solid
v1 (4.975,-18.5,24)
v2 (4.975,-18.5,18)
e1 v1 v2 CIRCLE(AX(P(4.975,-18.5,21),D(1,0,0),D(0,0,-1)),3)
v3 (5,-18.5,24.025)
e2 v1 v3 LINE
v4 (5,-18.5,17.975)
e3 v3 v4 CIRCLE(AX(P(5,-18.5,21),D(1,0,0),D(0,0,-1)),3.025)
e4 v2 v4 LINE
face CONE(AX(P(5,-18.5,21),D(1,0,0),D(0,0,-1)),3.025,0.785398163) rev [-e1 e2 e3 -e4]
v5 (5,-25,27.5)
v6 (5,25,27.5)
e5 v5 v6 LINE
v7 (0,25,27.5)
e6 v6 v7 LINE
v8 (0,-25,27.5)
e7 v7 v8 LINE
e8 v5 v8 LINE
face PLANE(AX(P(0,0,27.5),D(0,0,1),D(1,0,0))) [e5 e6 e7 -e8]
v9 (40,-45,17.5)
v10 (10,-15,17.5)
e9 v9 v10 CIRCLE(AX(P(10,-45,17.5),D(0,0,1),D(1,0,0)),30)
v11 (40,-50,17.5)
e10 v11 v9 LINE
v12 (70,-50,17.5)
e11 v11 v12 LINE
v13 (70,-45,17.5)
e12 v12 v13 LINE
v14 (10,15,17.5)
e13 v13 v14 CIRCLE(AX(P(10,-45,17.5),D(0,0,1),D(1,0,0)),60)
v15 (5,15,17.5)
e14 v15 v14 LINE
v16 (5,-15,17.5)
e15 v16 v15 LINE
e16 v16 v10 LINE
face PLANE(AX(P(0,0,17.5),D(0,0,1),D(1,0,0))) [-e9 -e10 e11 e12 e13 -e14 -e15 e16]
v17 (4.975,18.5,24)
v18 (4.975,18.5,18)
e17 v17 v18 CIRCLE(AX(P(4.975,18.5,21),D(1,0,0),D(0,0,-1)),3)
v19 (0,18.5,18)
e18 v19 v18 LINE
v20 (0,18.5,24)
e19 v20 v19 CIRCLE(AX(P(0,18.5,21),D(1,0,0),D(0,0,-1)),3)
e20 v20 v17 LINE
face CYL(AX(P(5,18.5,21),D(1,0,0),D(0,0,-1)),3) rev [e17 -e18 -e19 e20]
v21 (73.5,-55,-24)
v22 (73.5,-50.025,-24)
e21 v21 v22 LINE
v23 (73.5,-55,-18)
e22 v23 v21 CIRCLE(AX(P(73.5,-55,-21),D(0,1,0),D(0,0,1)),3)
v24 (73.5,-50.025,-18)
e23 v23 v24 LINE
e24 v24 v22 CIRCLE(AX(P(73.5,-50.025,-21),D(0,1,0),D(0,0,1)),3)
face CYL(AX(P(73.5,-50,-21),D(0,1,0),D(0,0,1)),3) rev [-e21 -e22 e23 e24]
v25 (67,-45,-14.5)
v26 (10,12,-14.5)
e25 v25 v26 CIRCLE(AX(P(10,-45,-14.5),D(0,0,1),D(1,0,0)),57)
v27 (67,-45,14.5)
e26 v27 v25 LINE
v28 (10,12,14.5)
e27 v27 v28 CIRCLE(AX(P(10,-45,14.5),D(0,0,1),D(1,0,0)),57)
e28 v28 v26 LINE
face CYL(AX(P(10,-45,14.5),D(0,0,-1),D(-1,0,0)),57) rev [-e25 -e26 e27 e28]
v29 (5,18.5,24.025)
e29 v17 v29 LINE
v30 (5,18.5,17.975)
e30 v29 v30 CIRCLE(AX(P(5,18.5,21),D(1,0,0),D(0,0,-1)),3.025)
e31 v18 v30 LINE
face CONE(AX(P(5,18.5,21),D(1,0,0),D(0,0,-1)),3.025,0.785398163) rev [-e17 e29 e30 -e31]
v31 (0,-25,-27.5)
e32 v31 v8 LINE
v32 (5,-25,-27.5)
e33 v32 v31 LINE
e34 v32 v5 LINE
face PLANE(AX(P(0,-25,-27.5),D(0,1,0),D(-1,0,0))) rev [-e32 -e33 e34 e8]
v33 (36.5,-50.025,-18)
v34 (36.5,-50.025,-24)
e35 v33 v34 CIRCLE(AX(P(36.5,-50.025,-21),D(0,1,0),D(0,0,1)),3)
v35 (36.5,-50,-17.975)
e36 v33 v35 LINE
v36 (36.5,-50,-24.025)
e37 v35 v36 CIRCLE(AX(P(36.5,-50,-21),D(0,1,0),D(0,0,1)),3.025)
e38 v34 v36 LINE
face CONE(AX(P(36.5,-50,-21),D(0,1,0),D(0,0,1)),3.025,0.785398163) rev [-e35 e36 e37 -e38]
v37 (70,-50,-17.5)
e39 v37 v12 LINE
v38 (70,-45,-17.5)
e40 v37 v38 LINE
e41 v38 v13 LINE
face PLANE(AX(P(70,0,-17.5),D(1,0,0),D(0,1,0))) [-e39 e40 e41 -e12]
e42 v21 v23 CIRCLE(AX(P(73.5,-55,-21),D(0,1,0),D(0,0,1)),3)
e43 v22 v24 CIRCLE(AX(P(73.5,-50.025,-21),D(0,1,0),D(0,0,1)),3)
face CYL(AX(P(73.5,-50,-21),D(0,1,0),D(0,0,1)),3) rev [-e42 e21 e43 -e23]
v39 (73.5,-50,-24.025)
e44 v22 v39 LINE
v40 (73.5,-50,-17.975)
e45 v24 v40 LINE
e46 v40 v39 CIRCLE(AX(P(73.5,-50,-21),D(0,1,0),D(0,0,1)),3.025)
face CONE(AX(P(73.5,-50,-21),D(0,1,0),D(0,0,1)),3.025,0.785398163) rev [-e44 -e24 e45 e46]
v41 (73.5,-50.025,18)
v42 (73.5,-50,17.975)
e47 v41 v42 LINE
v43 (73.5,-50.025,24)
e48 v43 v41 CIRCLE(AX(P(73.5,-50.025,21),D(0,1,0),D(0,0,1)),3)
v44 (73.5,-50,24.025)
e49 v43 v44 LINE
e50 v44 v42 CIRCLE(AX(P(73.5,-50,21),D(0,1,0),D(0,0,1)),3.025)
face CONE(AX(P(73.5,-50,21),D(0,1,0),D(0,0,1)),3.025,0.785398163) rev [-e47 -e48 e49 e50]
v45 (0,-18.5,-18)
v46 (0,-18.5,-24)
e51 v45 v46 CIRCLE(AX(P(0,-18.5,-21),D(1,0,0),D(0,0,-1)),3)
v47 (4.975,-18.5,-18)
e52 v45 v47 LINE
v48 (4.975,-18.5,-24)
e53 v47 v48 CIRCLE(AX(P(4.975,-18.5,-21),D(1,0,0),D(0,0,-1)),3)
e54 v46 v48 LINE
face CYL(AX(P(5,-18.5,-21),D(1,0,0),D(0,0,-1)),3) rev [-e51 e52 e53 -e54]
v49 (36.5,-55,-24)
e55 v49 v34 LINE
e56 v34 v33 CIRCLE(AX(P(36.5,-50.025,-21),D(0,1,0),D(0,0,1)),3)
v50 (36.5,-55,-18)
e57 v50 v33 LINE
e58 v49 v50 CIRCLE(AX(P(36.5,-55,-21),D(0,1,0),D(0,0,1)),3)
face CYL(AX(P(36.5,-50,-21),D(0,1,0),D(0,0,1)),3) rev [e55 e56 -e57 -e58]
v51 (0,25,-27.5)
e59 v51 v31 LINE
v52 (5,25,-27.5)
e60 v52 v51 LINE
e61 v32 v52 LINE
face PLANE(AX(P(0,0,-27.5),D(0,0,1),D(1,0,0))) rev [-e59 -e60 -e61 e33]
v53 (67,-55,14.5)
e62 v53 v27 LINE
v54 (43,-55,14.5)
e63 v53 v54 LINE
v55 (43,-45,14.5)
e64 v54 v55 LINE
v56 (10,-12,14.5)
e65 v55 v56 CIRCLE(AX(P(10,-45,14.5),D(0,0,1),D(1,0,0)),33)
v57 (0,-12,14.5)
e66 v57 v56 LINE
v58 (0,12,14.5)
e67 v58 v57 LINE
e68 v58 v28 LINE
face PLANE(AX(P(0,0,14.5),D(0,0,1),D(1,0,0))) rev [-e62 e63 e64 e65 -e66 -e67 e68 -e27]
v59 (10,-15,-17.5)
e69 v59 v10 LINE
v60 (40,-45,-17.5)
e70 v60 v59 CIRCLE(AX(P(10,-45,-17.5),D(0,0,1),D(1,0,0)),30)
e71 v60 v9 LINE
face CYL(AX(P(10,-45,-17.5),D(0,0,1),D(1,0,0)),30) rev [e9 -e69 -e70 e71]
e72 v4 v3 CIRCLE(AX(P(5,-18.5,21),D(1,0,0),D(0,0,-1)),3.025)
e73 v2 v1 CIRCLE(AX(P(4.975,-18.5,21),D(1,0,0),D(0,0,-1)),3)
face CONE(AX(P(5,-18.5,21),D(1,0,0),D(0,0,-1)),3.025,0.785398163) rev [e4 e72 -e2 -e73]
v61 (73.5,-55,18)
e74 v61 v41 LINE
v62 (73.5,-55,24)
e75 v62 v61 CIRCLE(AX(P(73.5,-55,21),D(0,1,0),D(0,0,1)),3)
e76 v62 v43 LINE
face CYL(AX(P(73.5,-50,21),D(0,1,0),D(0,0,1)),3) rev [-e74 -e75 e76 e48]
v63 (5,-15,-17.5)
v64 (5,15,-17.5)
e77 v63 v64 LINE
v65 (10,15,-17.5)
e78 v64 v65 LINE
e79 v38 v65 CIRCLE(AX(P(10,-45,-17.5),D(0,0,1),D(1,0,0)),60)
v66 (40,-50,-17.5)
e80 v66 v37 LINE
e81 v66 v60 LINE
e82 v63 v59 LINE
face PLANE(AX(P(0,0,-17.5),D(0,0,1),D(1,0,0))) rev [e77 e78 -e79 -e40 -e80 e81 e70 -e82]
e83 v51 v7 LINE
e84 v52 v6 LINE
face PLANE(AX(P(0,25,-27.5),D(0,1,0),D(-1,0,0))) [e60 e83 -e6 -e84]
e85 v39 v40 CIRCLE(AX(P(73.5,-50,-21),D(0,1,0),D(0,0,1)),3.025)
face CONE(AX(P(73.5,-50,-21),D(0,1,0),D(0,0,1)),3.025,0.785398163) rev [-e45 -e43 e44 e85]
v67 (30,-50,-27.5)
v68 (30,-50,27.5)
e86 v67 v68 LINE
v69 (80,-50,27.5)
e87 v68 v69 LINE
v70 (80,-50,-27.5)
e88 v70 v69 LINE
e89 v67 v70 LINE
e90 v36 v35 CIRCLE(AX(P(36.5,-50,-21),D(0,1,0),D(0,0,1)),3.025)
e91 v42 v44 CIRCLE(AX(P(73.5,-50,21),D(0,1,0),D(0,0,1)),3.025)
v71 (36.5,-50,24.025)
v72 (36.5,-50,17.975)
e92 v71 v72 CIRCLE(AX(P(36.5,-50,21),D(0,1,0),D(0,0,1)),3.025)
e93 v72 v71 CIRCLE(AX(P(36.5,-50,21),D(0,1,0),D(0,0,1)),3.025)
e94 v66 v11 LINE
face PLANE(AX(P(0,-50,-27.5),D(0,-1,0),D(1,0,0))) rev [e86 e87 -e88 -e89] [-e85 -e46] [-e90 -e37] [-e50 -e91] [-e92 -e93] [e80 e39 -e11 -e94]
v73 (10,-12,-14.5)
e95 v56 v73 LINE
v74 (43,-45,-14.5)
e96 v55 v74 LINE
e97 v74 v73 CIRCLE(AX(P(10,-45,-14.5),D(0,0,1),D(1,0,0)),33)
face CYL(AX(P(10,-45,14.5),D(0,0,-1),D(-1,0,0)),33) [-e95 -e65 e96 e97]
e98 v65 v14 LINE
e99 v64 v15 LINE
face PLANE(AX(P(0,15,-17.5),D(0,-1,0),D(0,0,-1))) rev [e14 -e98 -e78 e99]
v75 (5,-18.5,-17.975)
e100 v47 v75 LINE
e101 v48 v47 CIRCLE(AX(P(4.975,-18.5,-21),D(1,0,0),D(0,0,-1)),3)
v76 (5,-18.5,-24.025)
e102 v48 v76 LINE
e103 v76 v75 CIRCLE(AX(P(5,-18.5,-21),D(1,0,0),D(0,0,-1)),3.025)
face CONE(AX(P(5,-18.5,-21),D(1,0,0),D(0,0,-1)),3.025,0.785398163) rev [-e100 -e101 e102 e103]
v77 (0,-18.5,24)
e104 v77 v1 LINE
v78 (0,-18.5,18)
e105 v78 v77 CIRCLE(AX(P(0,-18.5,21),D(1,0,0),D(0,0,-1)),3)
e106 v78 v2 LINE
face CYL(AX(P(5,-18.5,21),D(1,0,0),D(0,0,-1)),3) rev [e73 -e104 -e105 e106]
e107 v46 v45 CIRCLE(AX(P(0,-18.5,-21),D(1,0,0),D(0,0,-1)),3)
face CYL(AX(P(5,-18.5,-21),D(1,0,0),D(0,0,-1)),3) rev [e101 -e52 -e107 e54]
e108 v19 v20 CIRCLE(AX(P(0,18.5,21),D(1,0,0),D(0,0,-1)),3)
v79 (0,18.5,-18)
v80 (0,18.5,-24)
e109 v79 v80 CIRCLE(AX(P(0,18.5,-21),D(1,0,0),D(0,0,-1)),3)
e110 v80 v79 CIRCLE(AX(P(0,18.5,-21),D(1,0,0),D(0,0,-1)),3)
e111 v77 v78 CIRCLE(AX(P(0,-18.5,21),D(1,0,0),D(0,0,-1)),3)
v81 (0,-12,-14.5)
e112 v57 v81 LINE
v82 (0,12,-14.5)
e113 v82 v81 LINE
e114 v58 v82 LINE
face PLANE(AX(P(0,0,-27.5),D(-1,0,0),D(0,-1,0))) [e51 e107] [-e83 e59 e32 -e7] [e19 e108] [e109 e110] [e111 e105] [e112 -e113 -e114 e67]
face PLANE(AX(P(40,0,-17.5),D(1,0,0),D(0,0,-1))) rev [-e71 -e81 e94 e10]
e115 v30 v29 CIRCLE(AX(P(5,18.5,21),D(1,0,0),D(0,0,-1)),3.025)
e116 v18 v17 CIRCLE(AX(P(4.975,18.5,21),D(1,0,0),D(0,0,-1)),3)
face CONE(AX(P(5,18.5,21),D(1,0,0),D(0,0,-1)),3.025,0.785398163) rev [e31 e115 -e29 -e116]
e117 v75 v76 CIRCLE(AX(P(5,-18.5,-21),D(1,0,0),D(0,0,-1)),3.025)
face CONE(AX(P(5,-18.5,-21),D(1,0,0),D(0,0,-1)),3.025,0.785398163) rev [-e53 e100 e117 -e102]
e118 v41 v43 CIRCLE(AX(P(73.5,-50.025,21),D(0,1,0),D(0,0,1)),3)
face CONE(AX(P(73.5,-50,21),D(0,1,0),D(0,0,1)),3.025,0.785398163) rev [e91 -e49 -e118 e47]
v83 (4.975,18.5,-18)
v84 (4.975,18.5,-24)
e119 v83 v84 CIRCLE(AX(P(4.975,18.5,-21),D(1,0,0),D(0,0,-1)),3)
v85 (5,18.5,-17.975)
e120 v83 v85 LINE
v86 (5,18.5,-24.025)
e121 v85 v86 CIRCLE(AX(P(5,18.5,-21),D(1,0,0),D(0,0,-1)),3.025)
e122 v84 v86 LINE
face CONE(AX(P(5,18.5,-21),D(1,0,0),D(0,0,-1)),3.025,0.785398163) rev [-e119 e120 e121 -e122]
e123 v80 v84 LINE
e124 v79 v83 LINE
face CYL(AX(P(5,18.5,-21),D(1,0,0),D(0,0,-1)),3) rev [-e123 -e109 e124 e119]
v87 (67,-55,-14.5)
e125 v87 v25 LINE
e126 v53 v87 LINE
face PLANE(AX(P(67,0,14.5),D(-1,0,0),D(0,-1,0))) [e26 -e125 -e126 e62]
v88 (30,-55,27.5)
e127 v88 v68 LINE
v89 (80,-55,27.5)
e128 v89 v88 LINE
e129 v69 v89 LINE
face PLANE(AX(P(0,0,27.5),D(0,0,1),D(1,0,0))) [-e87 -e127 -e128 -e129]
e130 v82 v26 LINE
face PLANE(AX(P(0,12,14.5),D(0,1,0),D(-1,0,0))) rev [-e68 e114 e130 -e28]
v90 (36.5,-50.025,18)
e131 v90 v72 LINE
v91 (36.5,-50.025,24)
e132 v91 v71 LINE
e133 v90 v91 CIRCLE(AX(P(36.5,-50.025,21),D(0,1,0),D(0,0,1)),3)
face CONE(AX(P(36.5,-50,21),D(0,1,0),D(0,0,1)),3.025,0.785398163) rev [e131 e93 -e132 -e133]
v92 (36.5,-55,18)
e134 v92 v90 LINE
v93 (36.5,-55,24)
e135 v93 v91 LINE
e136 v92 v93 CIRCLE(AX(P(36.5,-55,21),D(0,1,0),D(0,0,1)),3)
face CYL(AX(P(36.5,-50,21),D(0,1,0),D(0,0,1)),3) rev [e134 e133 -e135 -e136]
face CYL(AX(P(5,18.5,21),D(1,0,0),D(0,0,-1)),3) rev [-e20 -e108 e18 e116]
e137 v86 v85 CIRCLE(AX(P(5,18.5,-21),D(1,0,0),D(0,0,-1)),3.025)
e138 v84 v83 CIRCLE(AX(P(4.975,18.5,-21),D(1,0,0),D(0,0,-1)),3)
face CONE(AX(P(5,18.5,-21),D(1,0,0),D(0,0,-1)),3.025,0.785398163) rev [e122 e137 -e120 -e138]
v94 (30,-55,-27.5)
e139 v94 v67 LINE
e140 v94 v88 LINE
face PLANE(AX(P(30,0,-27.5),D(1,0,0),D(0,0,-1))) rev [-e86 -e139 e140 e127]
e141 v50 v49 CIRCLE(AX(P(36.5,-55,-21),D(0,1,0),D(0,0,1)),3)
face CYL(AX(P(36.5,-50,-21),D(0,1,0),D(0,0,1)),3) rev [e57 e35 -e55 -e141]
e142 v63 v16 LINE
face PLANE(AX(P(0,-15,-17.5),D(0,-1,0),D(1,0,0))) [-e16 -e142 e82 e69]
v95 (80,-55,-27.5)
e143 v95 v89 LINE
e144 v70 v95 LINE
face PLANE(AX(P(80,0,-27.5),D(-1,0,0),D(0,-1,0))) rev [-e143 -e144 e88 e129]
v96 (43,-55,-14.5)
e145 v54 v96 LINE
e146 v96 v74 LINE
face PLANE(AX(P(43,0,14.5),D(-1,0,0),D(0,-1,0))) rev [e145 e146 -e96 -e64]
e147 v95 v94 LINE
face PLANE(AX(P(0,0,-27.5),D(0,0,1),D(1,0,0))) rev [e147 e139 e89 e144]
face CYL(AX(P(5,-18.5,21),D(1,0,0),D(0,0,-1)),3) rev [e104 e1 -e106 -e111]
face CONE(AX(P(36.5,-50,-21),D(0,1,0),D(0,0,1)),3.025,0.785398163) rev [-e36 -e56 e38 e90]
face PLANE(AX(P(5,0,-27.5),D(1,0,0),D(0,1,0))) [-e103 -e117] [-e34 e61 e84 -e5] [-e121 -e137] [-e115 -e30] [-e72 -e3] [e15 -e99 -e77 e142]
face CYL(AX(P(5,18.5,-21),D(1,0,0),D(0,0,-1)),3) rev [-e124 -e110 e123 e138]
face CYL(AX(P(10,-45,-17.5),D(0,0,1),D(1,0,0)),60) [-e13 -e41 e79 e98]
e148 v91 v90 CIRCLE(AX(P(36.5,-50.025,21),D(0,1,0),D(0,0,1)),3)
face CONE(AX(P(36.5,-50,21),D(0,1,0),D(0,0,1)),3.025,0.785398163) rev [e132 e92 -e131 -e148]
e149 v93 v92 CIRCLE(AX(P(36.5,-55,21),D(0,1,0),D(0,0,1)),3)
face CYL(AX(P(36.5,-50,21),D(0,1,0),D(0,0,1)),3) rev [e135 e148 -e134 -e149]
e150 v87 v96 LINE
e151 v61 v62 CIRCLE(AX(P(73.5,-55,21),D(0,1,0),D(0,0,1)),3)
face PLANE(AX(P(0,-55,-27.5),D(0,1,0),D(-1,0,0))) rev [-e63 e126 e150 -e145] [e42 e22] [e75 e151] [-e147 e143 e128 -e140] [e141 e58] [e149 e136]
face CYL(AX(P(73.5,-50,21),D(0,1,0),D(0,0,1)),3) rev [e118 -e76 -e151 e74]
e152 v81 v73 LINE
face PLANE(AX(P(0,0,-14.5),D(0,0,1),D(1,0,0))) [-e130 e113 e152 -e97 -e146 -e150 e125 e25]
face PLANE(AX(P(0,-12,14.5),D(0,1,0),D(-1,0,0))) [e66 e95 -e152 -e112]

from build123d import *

# Parameters (mm, degrees)
CURVED_DUCT_BODY_DEPTH             = 17.5
SKETCH1_4_W                        = 50
SKETCH1_4_H                        = 5
SKETCH1_4_W_2                      = 5
SKETCH1_4_H_2                      = 50
MOUNTING_FLANGES_DEPTH             = 27.5
SKETCH1_5_W                        = 24
SKETCH1_5_H                        = 5
SKETCH1_5_W_2                      = 5
SKETCH1_5_H_2                      = 24
DUCT_RELIEF_CUT_29MM_DEPTH         = 14.5
DOWEL_HOLES_6_FLANGE_A_D           = 6
DOWEL_HOLES_6_FLANGE_A_CSINK_D     = 6.05
DOWEL_HOLES_6_FLANGE_A_CSINK_ANGLE = 90
DOWEL_HOLES_6_FLANGE_B_D           = 6
DOWEL_HOLES_6_FLANGE_B_CSINK_D     = 6.05
DOWEL_HOLES_6_FLANGE_B_CSINK_ANGLE = 90


with BuildPart() as part:
    # Bracket Profile Sketch → Curved Duct Body (new, symmetric)
    with BuildSketch(Plane.YX):
        with BuildLine():
            Line((15, 5), (15, 10))
            ThreePointArc((15, 10), (-2.573593129, 52.426406871), (-45, 70))
            Line((-45, 70), (-50, 70))
            Line((-50, 70), (-50, 40))
            Line((-50, 40), (-45, 40))
            ThreePointArc((-45, 40), (-23.786796564, 31.213203436), (-15, 10))
            Line((-15, 10), (-15, 5))
            Line((-15, 5), (15, 5))
        make_face()
    extrude(amount=CURVED_DUCT_BODY_DEPTH, both=True)

    # Sketch1_4 → Mounting Flanges (add, symmetric)
    with BuildSketch(Plane.YX):
        with Locations((0, 2.5)):
            Rectangle(SKETCH1_4_W, SKETCH1_4_H)
        with Locations((-52.5, 55)):
            Rectangle(SKETCH1_4_W_2, SKETCH1_4_H_2)
    extrude(amount=MOUNTING_FLANGES_DEPTH, both=True)

    # Sketch1_5 → Duct Relief Cut 29mm (cut, symmetric)
    with BuildSketch(Plane.YX):
        with BuildLine():
            Line((-12, 5), (12, 5))
            Line((12, 5), (12, 10))
            ThreePointArc((12, 10), (-4.694913472, 50.305086528), (-45, 67))
            Line((-45, 67), (-50, 67))
            Line((-50, 67), (-50, 43))
            Line((-50, 43), (-45, 43))
            ThreePointArc((-45, 43), (-21.665476221, 33.334523779), (-12, 10))
            Line((-12, 10), (-12, 5))
        make_face()
        with Locations((0, 2.5)):
            Rectangle(SKETCH1_5_W, SKETCH1_5_H)
        with Locations((-52.5, 55)):
            Rectangle(SKETCH1_5_W_2, SKETCH1_5_H_2)
    extrude(amount=DUCT_RELIEF_CUT_29MM_DEPTH, both=True, mode=Mode.SUBTRACT)

    # Dowel Holes _6 Flange A (through all)
    with Locations(Plane(origin=(5, 0, 0), x_dir=(0, 0, -1), z_dir=(1, 0, 0))):
        with Locations((-21, 18.5), (21, 18.5), (21, -18.5), (-21, -18.5)):
            CounterSinkHole(DOWEL_HOLES_6_FLANGE_A_D / 2, DOWEL_HOLES_6_FLANGE_A_CSINK_D / 2, counter_sink_angle=DOWEL_HOLES_6_FLANGE_A_CSINK_ANGLE)

    # Dowel Holes _6 Flange B (through all)
    with Locations(Plane(origin=(0, -50, 0), x_dir=(1, 0, 0), z_dir=(0, 1, 0))):
        with Locations((73.5, 21), (73.5, -21), (36.5, 21), (36.5, -21)):
            CounterSinkHole(DOWEL_HOLES_6_FLANGE_B_D / 2, DOWEL_HOLES_6_FLANGE_B_CSINK_D / 2, counter_sink_angle=DOWEL_HOLES_6_FLANGE_B_CSINK_ANGLE)


solid = part.part
